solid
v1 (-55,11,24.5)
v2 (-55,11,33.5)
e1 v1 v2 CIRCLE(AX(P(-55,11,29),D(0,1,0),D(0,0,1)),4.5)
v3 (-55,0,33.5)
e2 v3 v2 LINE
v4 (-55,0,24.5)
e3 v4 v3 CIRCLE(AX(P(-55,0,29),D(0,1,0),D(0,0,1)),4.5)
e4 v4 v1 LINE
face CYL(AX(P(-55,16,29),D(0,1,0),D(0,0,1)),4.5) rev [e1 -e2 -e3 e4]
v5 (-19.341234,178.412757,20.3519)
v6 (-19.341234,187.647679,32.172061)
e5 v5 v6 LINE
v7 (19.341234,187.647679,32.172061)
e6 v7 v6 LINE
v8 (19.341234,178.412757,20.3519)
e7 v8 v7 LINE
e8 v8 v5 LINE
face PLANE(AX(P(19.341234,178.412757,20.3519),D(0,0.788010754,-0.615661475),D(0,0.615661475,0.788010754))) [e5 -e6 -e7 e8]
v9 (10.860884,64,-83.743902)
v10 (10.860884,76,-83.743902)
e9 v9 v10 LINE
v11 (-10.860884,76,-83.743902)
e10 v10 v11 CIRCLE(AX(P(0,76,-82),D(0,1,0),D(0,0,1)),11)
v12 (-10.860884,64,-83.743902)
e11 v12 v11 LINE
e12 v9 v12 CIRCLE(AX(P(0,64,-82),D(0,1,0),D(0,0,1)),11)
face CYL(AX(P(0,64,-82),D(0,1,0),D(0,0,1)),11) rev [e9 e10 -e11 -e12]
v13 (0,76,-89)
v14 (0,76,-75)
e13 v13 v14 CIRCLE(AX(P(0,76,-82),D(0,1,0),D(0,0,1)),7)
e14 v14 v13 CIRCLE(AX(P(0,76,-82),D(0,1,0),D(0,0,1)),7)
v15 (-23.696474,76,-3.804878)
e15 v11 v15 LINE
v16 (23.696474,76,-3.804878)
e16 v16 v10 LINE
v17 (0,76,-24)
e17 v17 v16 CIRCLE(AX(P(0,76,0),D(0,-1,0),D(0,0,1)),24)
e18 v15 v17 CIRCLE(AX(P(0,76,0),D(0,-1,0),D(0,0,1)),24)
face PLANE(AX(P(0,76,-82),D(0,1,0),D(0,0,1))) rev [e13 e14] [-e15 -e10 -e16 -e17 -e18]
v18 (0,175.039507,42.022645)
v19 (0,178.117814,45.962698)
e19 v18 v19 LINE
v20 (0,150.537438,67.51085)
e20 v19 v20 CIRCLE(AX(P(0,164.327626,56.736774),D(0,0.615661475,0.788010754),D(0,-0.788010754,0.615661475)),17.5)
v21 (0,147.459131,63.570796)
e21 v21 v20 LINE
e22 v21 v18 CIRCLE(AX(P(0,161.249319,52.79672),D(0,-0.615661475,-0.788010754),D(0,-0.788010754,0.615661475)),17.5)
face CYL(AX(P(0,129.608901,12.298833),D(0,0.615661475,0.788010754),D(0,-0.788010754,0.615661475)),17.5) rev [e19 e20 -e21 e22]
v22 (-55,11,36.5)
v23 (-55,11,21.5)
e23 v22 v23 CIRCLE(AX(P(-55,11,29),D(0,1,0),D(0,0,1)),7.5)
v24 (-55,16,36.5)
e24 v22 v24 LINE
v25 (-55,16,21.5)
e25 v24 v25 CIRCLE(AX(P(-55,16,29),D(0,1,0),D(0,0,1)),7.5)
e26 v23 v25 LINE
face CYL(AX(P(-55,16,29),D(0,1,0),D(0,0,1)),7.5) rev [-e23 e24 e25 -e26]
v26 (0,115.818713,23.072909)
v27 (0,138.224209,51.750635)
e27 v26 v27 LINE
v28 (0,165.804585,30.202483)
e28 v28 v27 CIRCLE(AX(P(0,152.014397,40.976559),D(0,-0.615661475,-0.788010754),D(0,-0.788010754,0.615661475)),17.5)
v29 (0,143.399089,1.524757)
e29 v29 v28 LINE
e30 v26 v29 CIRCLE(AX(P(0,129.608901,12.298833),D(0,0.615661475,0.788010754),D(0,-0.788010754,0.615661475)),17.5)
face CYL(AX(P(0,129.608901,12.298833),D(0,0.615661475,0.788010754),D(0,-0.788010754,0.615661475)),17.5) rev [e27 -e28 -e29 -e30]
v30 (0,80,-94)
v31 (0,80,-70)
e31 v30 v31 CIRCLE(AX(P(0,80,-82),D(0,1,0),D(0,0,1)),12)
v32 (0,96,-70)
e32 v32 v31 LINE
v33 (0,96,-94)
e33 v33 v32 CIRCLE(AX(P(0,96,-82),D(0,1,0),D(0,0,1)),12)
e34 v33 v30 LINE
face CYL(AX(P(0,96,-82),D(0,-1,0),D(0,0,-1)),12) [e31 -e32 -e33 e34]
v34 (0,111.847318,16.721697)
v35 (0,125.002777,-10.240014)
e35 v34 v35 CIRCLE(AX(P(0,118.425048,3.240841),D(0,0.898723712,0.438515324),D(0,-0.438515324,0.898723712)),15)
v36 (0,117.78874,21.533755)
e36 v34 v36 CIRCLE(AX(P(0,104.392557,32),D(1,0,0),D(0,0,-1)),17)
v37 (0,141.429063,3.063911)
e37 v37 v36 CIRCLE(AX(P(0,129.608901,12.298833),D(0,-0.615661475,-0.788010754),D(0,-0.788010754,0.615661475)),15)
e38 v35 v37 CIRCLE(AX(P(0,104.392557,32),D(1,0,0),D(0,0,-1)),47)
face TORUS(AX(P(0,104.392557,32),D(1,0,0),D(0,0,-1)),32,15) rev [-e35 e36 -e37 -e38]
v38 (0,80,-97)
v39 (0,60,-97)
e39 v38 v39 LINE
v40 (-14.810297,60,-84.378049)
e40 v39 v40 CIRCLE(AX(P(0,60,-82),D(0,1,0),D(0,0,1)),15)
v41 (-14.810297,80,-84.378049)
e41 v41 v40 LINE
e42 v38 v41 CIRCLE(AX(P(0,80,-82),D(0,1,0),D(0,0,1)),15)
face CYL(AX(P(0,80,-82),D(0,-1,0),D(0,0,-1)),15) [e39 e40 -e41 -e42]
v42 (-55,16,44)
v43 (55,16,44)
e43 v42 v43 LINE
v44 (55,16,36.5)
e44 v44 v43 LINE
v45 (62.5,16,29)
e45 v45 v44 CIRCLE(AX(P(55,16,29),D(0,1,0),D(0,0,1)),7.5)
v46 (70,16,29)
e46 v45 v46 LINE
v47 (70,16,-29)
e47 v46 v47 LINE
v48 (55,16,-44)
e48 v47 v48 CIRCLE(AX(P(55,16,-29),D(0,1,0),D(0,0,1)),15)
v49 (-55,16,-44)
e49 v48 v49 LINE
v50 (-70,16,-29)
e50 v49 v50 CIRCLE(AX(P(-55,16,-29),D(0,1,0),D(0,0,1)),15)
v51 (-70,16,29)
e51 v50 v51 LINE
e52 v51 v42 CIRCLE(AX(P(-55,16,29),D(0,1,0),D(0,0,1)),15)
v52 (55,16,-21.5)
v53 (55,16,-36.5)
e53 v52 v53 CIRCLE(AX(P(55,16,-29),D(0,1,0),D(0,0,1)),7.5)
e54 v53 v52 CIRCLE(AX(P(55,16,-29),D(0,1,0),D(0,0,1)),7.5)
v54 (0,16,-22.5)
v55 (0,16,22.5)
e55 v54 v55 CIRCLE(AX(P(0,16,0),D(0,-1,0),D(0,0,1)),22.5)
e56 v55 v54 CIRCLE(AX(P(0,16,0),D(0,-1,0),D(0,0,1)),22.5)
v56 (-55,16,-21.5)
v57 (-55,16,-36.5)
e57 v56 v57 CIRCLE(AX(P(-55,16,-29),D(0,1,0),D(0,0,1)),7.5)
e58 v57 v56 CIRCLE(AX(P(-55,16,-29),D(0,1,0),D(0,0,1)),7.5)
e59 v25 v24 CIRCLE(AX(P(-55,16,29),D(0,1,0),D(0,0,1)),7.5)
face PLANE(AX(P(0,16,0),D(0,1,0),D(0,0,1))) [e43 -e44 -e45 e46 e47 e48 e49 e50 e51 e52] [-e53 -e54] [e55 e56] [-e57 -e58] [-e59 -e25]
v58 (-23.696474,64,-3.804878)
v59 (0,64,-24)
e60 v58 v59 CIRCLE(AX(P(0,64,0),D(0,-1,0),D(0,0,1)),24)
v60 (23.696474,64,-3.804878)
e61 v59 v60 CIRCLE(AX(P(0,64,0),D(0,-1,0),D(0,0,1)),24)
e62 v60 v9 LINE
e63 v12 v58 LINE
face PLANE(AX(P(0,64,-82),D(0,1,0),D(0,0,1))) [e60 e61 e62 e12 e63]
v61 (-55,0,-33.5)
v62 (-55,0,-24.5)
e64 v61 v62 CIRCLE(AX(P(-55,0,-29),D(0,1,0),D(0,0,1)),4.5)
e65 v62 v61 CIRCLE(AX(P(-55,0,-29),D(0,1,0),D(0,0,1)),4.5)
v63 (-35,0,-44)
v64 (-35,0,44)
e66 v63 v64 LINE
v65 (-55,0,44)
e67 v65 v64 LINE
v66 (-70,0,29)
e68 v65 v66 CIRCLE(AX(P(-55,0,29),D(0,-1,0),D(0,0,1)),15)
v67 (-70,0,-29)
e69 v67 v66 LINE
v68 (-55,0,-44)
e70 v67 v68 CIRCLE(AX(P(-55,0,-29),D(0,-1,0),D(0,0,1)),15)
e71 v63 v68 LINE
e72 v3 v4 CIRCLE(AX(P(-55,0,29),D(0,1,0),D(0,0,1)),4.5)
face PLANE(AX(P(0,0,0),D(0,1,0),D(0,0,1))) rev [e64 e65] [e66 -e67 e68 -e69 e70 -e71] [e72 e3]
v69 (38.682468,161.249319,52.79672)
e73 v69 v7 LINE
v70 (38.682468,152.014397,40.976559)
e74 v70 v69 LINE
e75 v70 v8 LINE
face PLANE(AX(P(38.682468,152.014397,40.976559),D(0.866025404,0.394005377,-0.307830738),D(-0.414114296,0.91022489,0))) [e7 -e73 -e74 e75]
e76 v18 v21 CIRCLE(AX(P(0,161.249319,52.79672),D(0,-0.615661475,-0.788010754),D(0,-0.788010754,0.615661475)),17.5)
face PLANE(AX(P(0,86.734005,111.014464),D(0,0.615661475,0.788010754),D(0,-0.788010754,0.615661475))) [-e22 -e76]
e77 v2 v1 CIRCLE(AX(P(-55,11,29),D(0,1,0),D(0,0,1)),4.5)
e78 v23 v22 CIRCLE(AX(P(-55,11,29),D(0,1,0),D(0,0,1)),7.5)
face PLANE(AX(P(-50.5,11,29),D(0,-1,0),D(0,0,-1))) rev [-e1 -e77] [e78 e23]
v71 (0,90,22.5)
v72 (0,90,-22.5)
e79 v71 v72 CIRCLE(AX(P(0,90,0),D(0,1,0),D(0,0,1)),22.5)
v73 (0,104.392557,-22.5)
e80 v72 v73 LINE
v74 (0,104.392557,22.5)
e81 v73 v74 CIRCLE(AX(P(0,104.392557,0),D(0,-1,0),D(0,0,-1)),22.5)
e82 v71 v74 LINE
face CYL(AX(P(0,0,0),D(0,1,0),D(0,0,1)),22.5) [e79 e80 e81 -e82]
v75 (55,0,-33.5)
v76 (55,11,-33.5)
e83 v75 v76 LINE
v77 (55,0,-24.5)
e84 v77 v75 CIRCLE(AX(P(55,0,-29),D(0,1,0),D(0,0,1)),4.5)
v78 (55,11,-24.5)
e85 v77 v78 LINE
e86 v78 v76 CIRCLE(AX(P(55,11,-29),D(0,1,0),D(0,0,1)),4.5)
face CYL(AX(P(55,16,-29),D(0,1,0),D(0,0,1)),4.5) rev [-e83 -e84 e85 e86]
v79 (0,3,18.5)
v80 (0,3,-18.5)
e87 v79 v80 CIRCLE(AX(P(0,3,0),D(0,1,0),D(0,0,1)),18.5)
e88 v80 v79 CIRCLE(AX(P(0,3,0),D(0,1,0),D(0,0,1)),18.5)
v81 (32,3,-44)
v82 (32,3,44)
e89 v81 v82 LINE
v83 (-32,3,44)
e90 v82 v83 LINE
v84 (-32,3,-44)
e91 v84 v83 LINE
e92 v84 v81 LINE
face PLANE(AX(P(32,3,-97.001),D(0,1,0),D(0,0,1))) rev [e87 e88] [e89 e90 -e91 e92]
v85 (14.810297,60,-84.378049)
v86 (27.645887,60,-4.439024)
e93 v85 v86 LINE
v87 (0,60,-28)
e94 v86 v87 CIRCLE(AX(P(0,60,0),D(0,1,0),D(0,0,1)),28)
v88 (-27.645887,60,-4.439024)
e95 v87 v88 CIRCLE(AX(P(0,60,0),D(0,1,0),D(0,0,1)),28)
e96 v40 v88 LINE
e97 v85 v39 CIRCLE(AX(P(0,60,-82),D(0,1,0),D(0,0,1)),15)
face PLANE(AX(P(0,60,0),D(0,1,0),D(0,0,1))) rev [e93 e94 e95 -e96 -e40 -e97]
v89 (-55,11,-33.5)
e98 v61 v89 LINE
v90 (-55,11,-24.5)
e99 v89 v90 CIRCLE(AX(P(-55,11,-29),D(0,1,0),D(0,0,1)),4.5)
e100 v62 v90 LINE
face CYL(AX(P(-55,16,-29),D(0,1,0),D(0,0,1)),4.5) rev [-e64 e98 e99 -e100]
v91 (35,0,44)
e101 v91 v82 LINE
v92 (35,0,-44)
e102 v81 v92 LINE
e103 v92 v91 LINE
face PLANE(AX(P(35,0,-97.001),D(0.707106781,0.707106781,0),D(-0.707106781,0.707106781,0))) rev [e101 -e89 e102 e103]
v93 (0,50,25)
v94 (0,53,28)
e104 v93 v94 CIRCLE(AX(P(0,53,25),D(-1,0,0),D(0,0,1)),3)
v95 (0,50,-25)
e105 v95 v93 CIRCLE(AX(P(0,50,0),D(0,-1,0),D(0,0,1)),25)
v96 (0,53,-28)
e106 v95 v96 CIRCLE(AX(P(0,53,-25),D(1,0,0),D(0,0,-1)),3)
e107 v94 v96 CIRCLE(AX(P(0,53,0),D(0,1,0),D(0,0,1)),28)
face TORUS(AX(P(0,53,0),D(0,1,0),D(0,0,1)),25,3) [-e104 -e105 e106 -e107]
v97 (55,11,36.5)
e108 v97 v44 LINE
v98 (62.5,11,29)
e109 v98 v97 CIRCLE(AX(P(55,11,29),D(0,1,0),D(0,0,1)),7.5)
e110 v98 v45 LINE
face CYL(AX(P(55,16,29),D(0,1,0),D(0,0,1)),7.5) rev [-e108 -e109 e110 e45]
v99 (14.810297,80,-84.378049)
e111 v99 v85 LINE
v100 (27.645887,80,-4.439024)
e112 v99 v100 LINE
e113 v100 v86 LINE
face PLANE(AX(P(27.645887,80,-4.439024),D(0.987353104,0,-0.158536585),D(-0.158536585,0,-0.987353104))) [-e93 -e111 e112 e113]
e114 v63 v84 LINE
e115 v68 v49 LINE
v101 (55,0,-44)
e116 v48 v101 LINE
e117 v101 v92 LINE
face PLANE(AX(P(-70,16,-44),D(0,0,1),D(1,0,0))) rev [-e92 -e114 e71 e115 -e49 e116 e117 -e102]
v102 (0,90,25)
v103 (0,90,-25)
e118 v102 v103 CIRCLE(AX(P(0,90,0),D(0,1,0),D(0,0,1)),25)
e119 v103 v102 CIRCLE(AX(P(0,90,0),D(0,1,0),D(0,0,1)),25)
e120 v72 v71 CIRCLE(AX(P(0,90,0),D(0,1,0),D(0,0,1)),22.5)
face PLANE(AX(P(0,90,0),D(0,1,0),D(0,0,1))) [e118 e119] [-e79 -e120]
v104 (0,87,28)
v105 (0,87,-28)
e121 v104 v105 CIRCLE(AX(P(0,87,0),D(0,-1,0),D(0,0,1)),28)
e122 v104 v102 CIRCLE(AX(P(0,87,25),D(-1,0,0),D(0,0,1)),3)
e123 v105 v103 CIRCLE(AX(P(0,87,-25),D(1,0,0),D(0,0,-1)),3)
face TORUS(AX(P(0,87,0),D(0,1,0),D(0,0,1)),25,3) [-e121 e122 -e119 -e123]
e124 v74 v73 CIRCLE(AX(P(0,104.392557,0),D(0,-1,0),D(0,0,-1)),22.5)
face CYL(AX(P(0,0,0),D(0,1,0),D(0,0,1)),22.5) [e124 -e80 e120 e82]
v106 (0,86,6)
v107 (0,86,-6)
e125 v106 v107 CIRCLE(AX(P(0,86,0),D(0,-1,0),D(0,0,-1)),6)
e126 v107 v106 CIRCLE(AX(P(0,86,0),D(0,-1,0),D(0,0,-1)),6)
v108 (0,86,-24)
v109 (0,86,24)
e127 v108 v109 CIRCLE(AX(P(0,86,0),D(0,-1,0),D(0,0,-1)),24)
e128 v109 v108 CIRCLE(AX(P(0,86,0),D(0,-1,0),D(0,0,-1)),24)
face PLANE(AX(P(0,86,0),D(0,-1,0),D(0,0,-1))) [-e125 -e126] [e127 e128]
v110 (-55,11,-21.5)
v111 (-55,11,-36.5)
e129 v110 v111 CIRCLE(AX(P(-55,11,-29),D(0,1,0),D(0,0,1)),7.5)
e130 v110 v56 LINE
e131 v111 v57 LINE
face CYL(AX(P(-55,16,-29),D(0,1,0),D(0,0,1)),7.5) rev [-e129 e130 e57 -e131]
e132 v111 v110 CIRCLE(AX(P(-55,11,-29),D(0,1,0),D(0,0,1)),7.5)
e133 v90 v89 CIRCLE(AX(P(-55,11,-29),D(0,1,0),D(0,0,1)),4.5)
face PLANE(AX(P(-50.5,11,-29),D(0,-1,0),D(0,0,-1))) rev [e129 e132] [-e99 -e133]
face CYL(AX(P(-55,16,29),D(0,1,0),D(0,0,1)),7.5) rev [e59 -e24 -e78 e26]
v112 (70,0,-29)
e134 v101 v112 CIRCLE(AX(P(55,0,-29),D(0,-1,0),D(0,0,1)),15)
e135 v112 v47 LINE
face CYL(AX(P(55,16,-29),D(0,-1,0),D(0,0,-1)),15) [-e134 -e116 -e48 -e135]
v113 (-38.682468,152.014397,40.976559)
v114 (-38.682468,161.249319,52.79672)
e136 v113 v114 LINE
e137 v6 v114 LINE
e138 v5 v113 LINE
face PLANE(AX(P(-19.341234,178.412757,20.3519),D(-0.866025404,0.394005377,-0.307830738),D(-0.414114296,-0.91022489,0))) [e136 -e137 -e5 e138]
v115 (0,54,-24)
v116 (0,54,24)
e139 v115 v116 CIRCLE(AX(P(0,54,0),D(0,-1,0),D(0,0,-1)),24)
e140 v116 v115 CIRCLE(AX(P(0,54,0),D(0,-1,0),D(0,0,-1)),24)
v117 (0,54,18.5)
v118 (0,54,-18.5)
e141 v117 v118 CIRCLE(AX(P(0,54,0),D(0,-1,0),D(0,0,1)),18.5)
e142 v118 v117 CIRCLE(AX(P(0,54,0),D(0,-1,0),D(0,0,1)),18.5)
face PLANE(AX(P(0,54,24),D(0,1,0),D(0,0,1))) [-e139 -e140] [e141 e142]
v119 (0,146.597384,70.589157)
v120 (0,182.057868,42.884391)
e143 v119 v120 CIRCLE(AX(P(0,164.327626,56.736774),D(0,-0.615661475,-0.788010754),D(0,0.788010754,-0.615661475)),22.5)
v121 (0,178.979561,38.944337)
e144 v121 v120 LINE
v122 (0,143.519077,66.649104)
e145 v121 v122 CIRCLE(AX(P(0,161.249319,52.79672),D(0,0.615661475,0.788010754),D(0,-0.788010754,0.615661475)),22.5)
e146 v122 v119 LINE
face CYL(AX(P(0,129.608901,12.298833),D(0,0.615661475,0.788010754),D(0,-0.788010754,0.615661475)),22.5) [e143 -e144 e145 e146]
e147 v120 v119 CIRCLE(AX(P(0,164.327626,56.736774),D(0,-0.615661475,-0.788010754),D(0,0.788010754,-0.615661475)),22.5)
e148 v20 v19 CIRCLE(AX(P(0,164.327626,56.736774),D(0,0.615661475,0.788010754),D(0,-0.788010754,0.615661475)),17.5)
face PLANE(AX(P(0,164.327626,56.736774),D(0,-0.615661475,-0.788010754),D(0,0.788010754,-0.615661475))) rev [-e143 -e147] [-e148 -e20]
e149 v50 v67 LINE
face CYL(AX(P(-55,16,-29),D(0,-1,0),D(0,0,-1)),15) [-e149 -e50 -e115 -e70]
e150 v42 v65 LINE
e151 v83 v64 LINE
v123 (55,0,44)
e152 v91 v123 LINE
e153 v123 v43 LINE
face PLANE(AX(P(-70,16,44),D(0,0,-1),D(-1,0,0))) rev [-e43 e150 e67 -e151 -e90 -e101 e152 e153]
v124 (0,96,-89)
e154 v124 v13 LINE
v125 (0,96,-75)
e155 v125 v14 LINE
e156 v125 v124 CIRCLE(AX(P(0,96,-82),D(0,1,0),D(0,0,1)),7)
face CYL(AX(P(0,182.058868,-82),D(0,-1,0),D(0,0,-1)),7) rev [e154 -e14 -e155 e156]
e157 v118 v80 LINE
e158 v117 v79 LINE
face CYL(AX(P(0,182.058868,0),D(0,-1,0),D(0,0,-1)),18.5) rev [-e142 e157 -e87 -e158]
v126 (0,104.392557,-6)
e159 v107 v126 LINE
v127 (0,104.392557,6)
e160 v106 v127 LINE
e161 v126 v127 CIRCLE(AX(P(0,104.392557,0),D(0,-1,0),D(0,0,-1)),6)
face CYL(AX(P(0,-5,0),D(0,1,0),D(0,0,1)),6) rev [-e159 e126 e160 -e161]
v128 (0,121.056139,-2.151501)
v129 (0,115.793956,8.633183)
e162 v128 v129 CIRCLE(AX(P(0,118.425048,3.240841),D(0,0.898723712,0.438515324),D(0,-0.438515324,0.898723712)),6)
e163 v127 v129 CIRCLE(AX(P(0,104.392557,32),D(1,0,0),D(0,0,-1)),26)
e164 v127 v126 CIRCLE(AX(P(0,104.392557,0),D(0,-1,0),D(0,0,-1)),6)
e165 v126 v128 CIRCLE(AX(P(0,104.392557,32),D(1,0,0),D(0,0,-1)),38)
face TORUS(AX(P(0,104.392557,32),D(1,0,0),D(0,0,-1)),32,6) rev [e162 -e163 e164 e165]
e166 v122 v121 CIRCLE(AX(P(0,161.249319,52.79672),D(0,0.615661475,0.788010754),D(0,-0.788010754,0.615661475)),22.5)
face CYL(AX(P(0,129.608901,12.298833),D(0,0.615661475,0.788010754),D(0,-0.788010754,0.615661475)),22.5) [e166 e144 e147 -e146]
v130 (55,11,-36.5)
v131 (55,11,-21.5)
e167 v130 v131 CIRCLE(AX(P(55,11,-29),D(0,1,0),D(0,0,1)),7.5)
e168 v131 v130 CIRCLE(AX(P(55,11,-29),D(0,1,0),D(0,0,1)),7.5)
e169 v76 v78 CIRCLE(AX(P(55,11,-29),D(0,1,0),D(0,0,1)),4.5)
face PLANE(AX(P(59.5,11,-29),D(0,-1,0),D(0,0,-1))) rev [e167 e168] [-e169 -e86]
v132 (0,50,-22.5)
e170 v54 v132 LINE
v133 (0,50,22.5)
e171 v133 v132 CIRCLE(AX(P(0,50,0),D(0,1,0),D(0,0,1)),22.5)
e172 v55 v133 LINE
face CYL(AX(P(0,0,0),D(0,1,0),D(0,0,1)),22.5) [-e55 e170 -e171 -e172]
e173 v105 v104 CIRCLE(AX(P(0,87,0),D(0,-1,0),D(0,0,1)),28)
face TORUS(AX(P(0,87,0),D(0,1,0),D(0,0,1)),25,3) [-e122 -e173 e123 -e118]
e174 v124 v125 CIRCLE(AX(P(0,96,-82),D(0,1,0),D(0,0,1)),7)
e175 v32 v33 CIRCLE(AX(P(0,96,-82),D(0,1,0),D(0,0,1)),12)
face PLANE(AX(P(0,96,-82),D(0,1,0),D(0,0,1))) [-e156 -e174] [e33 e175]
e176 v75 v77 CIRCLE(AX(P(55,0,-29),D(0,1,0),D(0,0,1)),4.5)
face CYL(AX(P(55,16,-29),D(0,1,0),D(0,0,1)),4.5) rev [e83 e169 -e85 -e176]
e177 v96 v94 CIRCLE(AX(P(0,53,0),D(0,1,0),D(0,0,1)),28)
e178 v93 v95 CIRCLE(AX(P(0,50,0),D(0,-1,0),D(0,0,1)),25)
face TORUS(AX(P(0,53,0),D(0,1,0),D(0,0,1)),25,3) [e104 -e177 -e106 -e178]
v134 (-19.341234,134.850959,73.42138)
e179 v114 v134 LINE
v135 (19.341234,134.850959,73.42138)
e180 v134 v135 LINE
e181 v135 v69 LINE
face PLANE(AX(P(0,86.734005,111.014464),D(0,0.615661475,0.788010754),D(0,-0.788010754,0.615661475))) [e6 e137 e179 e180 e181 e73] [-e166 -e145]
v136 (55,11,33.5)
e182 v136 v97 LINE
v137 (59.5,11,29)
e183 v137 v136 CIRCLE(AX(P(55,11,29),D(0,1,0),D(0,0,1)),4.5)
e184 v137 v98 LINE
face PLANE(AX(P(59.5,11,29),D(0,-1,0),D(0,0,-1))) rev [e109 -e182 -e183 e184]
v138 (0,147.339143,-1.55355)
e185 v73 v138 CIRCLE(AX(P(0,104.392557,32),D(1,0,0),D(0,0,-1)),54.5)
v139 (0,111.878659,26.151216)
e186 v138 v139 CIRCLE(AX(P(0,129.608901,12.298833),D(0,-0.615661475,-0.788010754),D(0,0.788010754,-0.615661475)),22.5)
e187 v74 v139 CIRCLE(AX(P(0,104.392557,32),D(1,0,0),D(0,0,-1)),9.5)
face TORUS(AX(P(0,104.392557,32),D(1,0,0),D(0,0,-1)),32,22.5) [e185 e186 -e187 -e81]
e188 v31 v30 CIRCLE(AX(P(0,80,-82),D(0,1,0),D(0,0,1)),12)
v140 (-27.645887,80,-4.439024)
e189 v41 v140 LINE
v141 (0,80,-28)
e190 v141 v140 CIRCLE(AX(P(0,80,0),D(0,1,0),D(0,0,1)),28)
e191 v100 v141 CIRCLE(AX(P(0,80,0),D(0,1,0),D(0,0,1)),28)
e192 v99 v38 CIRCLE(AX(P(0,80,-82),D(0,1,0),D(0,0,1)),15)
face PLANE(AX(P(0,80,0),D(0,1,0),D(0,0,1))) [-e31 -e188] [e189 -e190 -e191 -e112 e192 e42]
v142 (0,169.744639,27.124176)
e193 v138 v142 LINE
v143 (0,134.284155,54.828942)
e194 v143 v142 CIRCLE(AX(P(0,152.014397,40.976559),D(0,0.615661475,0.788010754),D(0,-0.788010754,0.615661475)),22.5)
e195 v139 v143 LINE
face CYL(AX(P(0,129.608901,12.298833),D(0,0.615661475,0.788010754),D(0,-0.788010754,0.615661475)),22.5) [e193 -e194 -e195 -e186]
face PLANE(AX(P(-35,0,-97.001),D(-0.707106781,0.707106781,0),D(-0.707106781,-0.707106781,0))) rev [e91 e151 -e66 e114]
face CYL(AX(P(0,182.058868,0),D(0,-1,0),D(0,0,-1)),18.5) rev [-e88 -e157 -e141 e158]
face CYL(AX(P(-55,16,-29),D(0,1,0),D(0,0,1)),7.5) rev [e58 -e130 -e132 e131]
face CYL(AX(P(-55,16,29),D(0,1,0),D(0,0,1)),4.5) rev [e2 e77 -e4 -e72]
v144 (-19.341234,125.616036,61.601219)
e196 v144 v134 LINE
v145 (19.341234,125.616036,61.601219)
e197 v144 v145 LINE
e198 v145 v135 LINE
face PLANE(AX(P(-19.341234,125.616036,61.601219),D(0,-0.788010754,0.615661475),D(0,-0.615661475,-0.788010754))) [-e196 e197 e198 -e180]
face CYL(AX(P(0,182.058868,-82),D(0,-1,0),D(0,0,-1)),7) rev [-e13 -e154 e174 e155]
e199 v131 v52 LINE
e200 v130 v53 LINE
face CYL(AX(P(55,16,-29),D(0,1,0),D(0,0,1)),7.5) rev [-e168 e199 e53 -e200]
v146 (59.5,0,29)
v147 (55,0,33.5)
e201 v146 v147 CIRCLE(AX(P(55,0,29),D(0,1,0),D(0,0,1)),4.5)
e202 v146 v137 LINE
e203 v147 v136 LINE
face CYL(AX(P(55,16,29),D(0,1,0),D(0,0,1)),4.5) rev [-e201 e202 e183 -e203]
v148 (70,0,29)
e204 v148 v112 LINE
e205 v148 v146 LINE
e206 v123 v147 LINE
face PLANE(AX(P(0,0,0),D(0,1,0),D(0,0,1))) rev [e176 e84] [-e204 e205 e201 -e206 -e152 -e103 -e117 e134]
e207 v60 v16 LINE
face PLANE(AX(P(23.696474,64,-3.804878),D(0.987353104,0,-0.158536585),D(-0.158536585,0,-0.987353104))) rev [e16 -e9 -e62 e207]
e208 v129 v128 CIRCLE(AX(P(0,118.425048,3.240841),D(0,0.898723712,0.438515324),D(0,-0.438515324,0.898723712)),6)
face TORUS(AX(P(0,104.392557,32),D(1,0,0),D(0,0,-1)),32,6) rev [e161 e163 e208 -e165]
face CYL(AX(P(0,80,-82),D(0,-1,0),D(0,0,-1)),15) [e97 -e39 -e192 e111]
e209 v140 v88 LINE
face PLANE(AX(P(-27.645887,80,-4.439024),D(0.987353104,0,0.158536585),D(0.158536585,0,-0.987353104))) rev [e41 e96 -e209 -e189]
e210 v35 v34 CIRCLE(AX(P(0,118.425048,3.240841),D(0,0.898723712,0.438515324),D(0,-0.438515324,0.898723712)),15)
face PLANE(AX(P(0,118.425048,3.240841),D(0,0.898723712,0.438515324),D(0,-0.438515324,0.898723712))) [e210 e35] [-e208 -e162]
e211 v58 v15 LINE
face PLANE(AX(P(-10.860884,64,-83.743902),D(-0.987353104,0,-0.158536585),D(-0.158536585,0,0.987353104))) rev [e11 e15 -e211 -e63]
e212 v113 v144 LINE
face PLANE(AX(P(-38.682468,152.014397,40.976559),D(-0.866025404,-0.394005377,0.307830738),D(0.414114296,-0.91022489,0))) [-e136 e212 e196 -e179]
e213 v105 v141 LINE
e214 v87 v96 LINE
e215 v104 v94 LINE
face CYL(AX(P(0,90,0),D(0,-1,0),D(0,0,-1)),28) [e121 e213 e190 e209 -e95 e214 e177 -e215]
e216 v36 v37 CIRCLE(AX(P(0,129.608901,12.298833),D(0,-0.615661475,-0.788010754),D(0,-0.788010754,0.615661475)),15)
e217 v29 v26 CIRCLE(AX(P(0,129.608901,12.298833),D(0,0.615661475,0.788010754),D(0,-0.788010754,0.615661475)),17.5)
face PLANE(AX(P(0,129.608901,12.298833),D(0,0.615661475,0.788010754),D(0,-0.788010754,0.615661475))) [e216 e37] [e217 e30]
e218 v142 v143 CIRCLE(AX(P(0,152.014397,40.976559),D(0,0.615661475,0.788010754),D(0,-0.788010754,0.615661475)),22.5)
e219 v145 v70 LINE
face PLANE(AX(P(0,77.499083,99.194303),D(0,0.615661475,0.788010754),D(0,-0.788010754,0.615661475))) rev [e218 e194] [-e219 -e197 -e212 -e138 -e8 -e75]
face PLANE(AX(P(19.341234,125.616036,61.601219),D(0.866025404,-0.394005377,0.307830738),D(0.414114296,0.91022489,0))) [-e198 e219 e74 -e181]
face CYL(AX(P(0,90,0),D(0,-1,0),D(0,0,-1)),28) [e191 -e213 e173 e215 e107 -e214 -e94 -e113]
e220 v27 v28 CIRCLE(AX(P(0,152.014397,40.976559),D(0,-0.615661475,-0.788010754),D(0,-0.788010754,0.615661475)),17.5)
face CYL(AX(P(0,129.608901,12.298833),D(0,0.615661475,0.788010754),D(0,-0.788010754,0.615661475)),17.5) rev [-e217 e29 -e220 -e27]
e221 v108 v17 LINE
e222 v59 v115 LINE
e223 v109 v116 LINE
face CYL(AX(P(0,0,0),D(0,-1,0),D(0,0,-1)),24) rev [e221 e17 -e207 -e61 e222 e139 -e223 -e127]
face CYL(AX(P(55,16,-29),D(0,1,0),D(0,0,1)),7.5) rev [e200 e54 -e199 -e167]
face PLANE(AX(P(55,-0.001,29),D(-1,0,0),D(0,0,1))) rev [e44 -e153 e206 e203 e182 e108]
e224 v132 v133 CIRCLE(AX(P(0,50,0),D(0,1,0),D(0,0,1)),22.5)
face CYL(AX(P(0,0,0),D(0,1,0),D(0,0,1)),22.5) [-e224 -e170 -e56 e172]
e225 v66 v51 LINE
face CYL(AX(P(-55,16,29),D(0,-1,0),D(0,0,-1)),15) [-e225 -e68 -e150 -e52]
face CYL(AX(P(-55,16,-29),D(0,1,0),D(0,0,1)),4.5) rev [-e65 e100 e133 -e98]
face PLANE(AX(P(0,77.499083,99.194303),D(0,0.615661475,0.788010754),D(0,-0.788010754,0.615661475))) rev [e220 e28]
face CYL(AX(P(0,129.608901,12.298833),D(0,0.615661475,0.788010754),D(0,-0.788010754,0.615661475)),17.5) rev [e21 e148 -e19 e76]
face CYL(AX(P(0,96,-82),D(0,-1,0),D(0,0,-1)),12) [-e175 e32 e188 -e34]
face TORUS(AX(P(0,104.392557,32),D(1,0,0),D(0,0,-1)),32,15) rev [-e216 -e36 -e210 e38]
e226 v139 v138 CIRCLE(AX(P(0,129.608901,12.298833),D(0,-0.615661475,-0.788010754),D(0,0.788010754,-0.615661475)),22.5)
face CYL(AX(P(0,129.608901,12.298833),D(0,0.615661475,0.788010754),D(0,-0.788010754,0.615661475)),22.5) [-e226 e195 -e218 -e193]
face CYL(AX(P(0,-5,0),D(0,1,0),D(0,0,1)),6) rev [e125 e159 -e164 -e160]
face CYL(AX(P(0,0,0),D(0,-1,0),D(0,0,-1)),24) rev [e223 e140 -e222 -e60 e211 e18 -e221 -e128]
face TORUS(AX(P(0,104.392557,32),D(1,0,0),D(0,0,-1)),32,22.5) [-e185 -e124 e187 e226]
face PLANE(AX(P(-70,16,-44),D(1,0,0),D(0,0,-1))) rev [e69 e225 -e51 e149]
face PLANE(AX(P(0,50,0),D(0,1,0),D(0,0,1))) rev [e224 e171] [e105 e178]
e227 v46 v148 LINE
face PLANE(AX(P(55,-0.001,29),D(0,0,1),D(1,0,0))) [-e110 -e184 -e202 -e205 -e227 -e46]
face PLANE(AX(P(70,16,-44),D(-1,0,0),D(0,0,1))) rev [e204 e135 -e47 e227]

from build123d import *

# Parameters (mm, degrees)
BASE_PLATE_SKETCH_W                = 140
BASE_PLATE_SKETCH_H                = 88
BASE_PLATE_DEPTH                   = 16
BASE_PLATE_CORNER_FILLETS_R15_R    = 15
MOUNTING_HOLES_CBORE_9_D           = 9
MOUNTING_HOLES_CBORE_9_CBORE_D     = 15
MOUNTING_HOLES_CBORE_9_CBORE_DEPTH = 5
BASE_BORE_37_DEPTH                 = 85.214013086
BASE_BORE_37_DEPTH_BACK            = 16
BASE_BORE_SKETCH_37_R              = 18.5
PIPE_ELBOW_45_PROFILE_R            = 22.5
COLUMN_START                       = 50
COLUMN_SKETCH_56_R                 = 28
COLUMN_56_DEPTH                    = 40
PIPE_ELBOW_BORE_PROFILE_R          = 6
LUG_ARM_DEPTH                      = 10
LUG_START                          = 10
SKETCH24_3_R                       = 12
LUG_BOSS_DEPTH                     = 16
LUG_HOLE_REACH                     = 165.908
SKETCH24_4_R                       = 7
LUG_ARM_GROOVE_DEPTH               = 6
COLUMN_GROOVE_PROFILE_W            = 24
COLUMN_GROOVE_PROFILE_H            = 32
COLUMN_BORE_37_REACH               = 219.84
COLUMN_BORE_SKETCH_37_R            = 18.5
ELBOW_PROFILE_CUT_PROFILE_R        = 15
OUTLET_BORE_PROFILE_R              = 17.5
BASE_RECESS_REACH                  = 242.678
HEX_START                          = -5
HEX_OUTLET_67_DEPTH                = 15
BASE_EDGE_NOTCH_REACH              = 211.217
COLUMN_FILLET_R3_R                 = 3


with BuildPart() as part:
    # Base Plate Sketch → Base Plate (new body)
    with BuildSketch(Plane(origin=(0, 0, 0), x_dir=(1, 0, 0), z_dir=(0, 1, 0))):
        Rectangle(BASE_PLATE_SKETCH_W, BASE_PLATE_SKETCH_H)
    extrude(amount=BASE_PLATE_DEPTH)

    # Base Plate Corner Fillets R15
    base_plate_corner_fillets_r15_edges = [part.edges().sort_by_distance(p)[0] for p in [
        (70, 8, 44),
        (-70, 8, 44),
        (-70, 8, -44),
        (70, 8, -44),
    ]]
    fillet(base_plate_corner_fillets_r15_edges, radius=BASE_PLATE_CORNER_FILLETS_R15_R)

    # Mounting Holes CBore _9 (through all)
    with Locations(Plane(origin=(0, 16, 0), x_dir=(1, 0, 0), z_dir=(0, 1, 0))):
        with Locations((-55, 29), (-55, -29), (55, -29), (55, 29)):
            CounterBoreHole(MOUNTING_HOLES_CBORE_9_D / 2, MOUNTING_HOLES_CBORE_9_CBORE_D / 2, MOUNTING_HOLES_CBORE_9_CBORE_DEPTH)

    # Base Bore Sketch _37 → Base Bore _37 (cut, two sides: drawn at the far end of the back side and taken through both)
    with BuildSketch(Plane.XZ.offset(-BASE_BORE_37_DEPTH_BACK)):
        with Locations(Location((0, 0, 0), (0, 0, 270))):
            Circle(BASE_BORE_SKETCH_37_R)
    extrude(amount=BASE_BORE_37_DEPTH + BASE_BORE_37_DEPTH_BACK, mode=Mode.SUBTRACT)

    # Pipe Elbow _45: sweep along a path in Pipe Elbow Path
    with BuildLine(Plane(origin=(0, 0, 0), x_dir=(0, 0, -1), z_dir=(1, 0, 0))) as pipe_elbow_45_path:
        Line((0, 0), (0, 104.392557166))
        ThreePointArc((0, 104.392557166), (-3.238590518, 118.420433863), (-12.29883279, 129.608901281))
        Line((-12.29883279, 129.608901281), (-56.73677426, 164.327626223))
    # Pipe Elbow _45 profile (on start of the path) → Pipe Elbow _45 (sweep)
    with BuildSketch(Plane.ZX):
        Circle(PIPE_ELBOW_45_PROFILE_R)
    sweep(path=pipe_elbow_45_path.line)

    # Column Sketch _56 → Column _56 (add)
    with BuildSketch(Plane(origin=(0, 0, 0), x_dir=(1, 0, 0), z_dir=(0, 1, 0)).offset(COLUMN_START)):
        with Locations(Location((0, 0, 0), (0, 0, 270))):
            Circle(COLUMN_SKETCH_56_R)
    extrude(amount=COLUMN_56_DEPTH)

    # Pipe Elbow Bore: sweep along a path in Sketch8_4
    with BuildLine(Plane(origin=(0, 0, 0), x_dir=(0, 0, -1), z_dir=(1, 0, 0))) as pipe_elbow_bore_path:
        Line((0, 0), (0, 104.392557166))
        ThreePointArc((0, 104.392557166), (-3.238590518, 118.420433863), (-12.29883279, 129.608901281))
        Line((-12.29883279, 129.608901281), (-56.73677426, 164.327626223))
    # Pipe Elbow Bore profile (on start of the path) → Pipe Elbow Bore (sweep, cut)
    with BuildSketch(Plane.ZX):
        Circle(PIPE_ELBOW_BORE_PROFILE_R)
    sweep(path=pipe_elbow_bore_path.line, mode=Mode.SUBTRACT)

    # Lug Arm Sketch → Lug Arm (add, symmetric)
    with BuildSketch(Plane(origin=(0, 70, 0), x_dir=(1, 0, 0), z_dir=(0, 1, 0))):
        with BuildLine():
            Line((27.6458869, 4.43902439), (14.810296553, 84.37804878))
            ThreePointArc((14.810296553, 84.37804878), (0, 97), (-14.810296553, 84.37804878))
            Line((-14.810296553, 84.37804878), (-27.6458869, 4.43902439))
            ThreePointArc((-27.6458869, 4.43902439), (0, 28), (27.6458869, 4.43902439))
        make_face()
    extrude(amount=LUG_ARM_DEPTH, both=True)

    # Sketch24_3 → Lug Boss (add)
    with BuildSketch(Plane(origin=(0, 70, 0), x_dir=(1, 0, 0), z_dir=(0, 1, 0)).offset(LUG_START)):
        with Locations(Location((0, 82, 0), (0, 0, 270))):
            Circle(SKETCH24_3_R)
    extrude(amount=LUG_BOSS_DEPTH)

    # Sketch24_4 → Lug Hole (cut, up to next)
    with BuildSketch(Plane(origin=(0, 70, 0), x_dir=(1, 0, 0), z_dir=(0, 1, 0)), mode=Mode.PRIVATE) as lug_hole_sk1:
        with Locations(Location((0, 82, 0), (0, 0, 270))):
            Circle(SKETCH24_4_R)
    lug_hole_tool1 = extrude(lug_hole_sk1.sketch, amount=LUG_HOLE_REACH, mode=Mode.PRIVATE) & part.part
    add(lug_hole_tool1.solids().sort_by_distance((0, 70, -82))[0], mode=Mode.SUBTRACT)

    # Lug Arm Groove Sketch → Lug Arm Groove (cut, symmetric)
    with BuildSketch(Plane(origin=(0, 70, 0), x_dir=(1, 0, 0), z_dir=(0, 1, 0))):
        with BuildLine():
            Line((23.696474485, 3.804878049), (10.860884139, 83.743902439))
            ThreePointArc((10.860884139, 83.743902439), (0, 93), (-10.860884139, 83.743902439))
            Line((-10.860884139, 83.743902439), (-23.696474485, 3.804878049))
            ThreePointArc((-23.696474485, 3.804878049), (0, 24), (23.696474485, 3.804878049))
        make_face()
    extrude(amount=LUG_ARM_GROOVE_DEPTH, both=True, mode=Mode.SUBTRACT)

    # Column Groove Profile → Column Groove (revolve, cut)
    with BuildSketch(Plane(origin=(0, 0, 0), x_dir=(0, 0, -1), z_dir=(1, 0, 0)), mode=Mode.PRIVATE) as column_groove_sk:
        with Locations((-12, 70)):
            Rectangle(COLUMN_GROOVE_PROFILE_W, COLUMN_GROOVE_PROFILE_H)
    revolve(column_groove_sk.sketch.rotate(Axis((0, 0, 0), (0, 1, 0)), 180), axis=Axis((0, 0, 0), (0, 1, 0)), mode=Mode.SUBTRACT)

    # Column Bore Sketch _37 → Column Bore _37 (cut, up to next)
    with BuildSketch(Plane.XZ, mode=Mode.PRIVATE) as column_bore_37_sk1:
        with Locations(Location((0, 0, 0), (0, 0, 270))):
            Circle(COLUMN_BORE_SKETCH_37_R)
    column_bore_37_tool1 = extrude(column_bore_37_sk1.sketch, amount=-COLUMN_BORE_37_REACH, mode=Mode.PRIVATE) & part.part
    add(column_bore_37_tool1.solids().sort_by_distance((0, 0, 0))[0], mode=Mode.SUBTRACT)

    # Elbow Profile Cut: sweep along a path in Elbow Profile Cut Sketch
    with BuildLine(Plane(origin=(0, 0, 0), x_dir=(0, 0, -1), z_dir=(1, 0, 0))) as elbow_profile_cut_path:
        ThreePointArc((-3.240841211, 118.425047527), (-7.132944581, 124.532804305), (-12.29883279, 129.608901281))
    # Elbow Profile Cut profile (on start of the path) → Elbow Profile Cut (sweep, cut)
    with BuildSketch(Plane(origin=(0, 118.425047527, 3.240841211), x_dir=(0, -0.4385153237962811, 0.898723712158438), z_dir=(0, 0.898723712158438, 0.4385153237962811))):
        Circle(ELBOW_PROFILE_CUT_PROFILE_R)
    sweep(path=elbow_profile_cut_path.line, mode=Mode.SUBTRACT)

    # Outlet Bore: sweep along a path in Outlet Bore Path
    with BuildLine(Plane(origin=(0, 0, 0), x_dir=(0, 0, -1), z_dir=(1, 0, 0))) as outlet_bore_path:
        Line((-12.29883279, 129.608901281), (-56.73677426, 164.327626223))
    # Outlet Bore profile (on start of the path) → Outlet Bore (sweep, cut)
    with BuildSketch(Plane(origin=(0, 129.608901281, 12.29883279), x_dir=(0, 0.7880107536067169, -0.6156614753256648), z_dir=(0, 0.6156614753256648, 0.7880107536067169))):
        Circle(OUTLET_BORE_PROFILE_R)
    sweep(path=outlet_bore_path.line, mode=Mode.SUBTRACT)

    # Base Recess Sketch → Base Recess (cut, up to next)
    with BuildSketch(Plane.XY.offset(44), mode=Mode.PRIVATE) as base_recess_sk1:
        Polygon((35, 0), (-35, 0), (-32, 3), (32, 3), align=None)
    base_recess_tool1 = extrude(base_recess_sk1.sketch, amount=-BASE_RECESS_REACH, mode=Mode.PRIVATE) & part.part
    add(base_recess_tool1.solids().sort_by_distance((0, 1.477612, 44))[0], mode=Mode.SUBTRACT)

    # Hex Outlet Sketch 67 → Hex Outlet 67 (add)
    with BuildSketch(Plane(origin=(0, 89.812312487, 114.954517836), x_dir=(1, 0, 0), z_dir=(0, 0.6156614753256595, 0.7880107536067211)).offset(HEX_START)):
        Polygon((38.682468036, 94.561290433), (19.341234018, 128.061290433), (-19.341234018, 128.061290433), (-38.682468036, 94.561290433), (-19.341234018, 61.061290433), (19.341234018, 61.061290433), align=None)
    extrude(amount=-HEX_OUTLET_67_DEPTH)

    # Base Edge Notch Sketch → Base Edge Notch (cut, up to next)
    with BuildSketch(Plane(origin=(0, 16, 0), x_dir=(1, 0, 0), z_dir=(0, 1, 0)), mode=Mode.PRIVATE) as base_edge_notch_sk1:
        with BuildLine():
            Line((55, -29), (70, -29))
            ThreePointArc((70, -29), (65.606601718, -39.606601718), (55, -44))
            Line((55, -44), (55, -29))
        make_face()
    base_edge_notch_tool1 = extrude(base_edge_notch_sk1.sketch, amount=-BASE_EDGE_NOTCH_REACH, mode=Mode.PRIVATE) & part.part
    add(base_edge_notch_tool1.solids().sort_by_distance((61.366198, 16, 35.366198))[0], mode=Mode.SUBTRACT)

    # Column Fillet R3
    column_fillet_r3_edges = [part.edges().sort_by_distance(p)[0] for p in [
        (0, 50, -28),
        (0, 90, -28),
    ]]
    fillet(column_fillet_r3_edges, radius=COLUMN_FILLET_R3_R)


solid = part.part
